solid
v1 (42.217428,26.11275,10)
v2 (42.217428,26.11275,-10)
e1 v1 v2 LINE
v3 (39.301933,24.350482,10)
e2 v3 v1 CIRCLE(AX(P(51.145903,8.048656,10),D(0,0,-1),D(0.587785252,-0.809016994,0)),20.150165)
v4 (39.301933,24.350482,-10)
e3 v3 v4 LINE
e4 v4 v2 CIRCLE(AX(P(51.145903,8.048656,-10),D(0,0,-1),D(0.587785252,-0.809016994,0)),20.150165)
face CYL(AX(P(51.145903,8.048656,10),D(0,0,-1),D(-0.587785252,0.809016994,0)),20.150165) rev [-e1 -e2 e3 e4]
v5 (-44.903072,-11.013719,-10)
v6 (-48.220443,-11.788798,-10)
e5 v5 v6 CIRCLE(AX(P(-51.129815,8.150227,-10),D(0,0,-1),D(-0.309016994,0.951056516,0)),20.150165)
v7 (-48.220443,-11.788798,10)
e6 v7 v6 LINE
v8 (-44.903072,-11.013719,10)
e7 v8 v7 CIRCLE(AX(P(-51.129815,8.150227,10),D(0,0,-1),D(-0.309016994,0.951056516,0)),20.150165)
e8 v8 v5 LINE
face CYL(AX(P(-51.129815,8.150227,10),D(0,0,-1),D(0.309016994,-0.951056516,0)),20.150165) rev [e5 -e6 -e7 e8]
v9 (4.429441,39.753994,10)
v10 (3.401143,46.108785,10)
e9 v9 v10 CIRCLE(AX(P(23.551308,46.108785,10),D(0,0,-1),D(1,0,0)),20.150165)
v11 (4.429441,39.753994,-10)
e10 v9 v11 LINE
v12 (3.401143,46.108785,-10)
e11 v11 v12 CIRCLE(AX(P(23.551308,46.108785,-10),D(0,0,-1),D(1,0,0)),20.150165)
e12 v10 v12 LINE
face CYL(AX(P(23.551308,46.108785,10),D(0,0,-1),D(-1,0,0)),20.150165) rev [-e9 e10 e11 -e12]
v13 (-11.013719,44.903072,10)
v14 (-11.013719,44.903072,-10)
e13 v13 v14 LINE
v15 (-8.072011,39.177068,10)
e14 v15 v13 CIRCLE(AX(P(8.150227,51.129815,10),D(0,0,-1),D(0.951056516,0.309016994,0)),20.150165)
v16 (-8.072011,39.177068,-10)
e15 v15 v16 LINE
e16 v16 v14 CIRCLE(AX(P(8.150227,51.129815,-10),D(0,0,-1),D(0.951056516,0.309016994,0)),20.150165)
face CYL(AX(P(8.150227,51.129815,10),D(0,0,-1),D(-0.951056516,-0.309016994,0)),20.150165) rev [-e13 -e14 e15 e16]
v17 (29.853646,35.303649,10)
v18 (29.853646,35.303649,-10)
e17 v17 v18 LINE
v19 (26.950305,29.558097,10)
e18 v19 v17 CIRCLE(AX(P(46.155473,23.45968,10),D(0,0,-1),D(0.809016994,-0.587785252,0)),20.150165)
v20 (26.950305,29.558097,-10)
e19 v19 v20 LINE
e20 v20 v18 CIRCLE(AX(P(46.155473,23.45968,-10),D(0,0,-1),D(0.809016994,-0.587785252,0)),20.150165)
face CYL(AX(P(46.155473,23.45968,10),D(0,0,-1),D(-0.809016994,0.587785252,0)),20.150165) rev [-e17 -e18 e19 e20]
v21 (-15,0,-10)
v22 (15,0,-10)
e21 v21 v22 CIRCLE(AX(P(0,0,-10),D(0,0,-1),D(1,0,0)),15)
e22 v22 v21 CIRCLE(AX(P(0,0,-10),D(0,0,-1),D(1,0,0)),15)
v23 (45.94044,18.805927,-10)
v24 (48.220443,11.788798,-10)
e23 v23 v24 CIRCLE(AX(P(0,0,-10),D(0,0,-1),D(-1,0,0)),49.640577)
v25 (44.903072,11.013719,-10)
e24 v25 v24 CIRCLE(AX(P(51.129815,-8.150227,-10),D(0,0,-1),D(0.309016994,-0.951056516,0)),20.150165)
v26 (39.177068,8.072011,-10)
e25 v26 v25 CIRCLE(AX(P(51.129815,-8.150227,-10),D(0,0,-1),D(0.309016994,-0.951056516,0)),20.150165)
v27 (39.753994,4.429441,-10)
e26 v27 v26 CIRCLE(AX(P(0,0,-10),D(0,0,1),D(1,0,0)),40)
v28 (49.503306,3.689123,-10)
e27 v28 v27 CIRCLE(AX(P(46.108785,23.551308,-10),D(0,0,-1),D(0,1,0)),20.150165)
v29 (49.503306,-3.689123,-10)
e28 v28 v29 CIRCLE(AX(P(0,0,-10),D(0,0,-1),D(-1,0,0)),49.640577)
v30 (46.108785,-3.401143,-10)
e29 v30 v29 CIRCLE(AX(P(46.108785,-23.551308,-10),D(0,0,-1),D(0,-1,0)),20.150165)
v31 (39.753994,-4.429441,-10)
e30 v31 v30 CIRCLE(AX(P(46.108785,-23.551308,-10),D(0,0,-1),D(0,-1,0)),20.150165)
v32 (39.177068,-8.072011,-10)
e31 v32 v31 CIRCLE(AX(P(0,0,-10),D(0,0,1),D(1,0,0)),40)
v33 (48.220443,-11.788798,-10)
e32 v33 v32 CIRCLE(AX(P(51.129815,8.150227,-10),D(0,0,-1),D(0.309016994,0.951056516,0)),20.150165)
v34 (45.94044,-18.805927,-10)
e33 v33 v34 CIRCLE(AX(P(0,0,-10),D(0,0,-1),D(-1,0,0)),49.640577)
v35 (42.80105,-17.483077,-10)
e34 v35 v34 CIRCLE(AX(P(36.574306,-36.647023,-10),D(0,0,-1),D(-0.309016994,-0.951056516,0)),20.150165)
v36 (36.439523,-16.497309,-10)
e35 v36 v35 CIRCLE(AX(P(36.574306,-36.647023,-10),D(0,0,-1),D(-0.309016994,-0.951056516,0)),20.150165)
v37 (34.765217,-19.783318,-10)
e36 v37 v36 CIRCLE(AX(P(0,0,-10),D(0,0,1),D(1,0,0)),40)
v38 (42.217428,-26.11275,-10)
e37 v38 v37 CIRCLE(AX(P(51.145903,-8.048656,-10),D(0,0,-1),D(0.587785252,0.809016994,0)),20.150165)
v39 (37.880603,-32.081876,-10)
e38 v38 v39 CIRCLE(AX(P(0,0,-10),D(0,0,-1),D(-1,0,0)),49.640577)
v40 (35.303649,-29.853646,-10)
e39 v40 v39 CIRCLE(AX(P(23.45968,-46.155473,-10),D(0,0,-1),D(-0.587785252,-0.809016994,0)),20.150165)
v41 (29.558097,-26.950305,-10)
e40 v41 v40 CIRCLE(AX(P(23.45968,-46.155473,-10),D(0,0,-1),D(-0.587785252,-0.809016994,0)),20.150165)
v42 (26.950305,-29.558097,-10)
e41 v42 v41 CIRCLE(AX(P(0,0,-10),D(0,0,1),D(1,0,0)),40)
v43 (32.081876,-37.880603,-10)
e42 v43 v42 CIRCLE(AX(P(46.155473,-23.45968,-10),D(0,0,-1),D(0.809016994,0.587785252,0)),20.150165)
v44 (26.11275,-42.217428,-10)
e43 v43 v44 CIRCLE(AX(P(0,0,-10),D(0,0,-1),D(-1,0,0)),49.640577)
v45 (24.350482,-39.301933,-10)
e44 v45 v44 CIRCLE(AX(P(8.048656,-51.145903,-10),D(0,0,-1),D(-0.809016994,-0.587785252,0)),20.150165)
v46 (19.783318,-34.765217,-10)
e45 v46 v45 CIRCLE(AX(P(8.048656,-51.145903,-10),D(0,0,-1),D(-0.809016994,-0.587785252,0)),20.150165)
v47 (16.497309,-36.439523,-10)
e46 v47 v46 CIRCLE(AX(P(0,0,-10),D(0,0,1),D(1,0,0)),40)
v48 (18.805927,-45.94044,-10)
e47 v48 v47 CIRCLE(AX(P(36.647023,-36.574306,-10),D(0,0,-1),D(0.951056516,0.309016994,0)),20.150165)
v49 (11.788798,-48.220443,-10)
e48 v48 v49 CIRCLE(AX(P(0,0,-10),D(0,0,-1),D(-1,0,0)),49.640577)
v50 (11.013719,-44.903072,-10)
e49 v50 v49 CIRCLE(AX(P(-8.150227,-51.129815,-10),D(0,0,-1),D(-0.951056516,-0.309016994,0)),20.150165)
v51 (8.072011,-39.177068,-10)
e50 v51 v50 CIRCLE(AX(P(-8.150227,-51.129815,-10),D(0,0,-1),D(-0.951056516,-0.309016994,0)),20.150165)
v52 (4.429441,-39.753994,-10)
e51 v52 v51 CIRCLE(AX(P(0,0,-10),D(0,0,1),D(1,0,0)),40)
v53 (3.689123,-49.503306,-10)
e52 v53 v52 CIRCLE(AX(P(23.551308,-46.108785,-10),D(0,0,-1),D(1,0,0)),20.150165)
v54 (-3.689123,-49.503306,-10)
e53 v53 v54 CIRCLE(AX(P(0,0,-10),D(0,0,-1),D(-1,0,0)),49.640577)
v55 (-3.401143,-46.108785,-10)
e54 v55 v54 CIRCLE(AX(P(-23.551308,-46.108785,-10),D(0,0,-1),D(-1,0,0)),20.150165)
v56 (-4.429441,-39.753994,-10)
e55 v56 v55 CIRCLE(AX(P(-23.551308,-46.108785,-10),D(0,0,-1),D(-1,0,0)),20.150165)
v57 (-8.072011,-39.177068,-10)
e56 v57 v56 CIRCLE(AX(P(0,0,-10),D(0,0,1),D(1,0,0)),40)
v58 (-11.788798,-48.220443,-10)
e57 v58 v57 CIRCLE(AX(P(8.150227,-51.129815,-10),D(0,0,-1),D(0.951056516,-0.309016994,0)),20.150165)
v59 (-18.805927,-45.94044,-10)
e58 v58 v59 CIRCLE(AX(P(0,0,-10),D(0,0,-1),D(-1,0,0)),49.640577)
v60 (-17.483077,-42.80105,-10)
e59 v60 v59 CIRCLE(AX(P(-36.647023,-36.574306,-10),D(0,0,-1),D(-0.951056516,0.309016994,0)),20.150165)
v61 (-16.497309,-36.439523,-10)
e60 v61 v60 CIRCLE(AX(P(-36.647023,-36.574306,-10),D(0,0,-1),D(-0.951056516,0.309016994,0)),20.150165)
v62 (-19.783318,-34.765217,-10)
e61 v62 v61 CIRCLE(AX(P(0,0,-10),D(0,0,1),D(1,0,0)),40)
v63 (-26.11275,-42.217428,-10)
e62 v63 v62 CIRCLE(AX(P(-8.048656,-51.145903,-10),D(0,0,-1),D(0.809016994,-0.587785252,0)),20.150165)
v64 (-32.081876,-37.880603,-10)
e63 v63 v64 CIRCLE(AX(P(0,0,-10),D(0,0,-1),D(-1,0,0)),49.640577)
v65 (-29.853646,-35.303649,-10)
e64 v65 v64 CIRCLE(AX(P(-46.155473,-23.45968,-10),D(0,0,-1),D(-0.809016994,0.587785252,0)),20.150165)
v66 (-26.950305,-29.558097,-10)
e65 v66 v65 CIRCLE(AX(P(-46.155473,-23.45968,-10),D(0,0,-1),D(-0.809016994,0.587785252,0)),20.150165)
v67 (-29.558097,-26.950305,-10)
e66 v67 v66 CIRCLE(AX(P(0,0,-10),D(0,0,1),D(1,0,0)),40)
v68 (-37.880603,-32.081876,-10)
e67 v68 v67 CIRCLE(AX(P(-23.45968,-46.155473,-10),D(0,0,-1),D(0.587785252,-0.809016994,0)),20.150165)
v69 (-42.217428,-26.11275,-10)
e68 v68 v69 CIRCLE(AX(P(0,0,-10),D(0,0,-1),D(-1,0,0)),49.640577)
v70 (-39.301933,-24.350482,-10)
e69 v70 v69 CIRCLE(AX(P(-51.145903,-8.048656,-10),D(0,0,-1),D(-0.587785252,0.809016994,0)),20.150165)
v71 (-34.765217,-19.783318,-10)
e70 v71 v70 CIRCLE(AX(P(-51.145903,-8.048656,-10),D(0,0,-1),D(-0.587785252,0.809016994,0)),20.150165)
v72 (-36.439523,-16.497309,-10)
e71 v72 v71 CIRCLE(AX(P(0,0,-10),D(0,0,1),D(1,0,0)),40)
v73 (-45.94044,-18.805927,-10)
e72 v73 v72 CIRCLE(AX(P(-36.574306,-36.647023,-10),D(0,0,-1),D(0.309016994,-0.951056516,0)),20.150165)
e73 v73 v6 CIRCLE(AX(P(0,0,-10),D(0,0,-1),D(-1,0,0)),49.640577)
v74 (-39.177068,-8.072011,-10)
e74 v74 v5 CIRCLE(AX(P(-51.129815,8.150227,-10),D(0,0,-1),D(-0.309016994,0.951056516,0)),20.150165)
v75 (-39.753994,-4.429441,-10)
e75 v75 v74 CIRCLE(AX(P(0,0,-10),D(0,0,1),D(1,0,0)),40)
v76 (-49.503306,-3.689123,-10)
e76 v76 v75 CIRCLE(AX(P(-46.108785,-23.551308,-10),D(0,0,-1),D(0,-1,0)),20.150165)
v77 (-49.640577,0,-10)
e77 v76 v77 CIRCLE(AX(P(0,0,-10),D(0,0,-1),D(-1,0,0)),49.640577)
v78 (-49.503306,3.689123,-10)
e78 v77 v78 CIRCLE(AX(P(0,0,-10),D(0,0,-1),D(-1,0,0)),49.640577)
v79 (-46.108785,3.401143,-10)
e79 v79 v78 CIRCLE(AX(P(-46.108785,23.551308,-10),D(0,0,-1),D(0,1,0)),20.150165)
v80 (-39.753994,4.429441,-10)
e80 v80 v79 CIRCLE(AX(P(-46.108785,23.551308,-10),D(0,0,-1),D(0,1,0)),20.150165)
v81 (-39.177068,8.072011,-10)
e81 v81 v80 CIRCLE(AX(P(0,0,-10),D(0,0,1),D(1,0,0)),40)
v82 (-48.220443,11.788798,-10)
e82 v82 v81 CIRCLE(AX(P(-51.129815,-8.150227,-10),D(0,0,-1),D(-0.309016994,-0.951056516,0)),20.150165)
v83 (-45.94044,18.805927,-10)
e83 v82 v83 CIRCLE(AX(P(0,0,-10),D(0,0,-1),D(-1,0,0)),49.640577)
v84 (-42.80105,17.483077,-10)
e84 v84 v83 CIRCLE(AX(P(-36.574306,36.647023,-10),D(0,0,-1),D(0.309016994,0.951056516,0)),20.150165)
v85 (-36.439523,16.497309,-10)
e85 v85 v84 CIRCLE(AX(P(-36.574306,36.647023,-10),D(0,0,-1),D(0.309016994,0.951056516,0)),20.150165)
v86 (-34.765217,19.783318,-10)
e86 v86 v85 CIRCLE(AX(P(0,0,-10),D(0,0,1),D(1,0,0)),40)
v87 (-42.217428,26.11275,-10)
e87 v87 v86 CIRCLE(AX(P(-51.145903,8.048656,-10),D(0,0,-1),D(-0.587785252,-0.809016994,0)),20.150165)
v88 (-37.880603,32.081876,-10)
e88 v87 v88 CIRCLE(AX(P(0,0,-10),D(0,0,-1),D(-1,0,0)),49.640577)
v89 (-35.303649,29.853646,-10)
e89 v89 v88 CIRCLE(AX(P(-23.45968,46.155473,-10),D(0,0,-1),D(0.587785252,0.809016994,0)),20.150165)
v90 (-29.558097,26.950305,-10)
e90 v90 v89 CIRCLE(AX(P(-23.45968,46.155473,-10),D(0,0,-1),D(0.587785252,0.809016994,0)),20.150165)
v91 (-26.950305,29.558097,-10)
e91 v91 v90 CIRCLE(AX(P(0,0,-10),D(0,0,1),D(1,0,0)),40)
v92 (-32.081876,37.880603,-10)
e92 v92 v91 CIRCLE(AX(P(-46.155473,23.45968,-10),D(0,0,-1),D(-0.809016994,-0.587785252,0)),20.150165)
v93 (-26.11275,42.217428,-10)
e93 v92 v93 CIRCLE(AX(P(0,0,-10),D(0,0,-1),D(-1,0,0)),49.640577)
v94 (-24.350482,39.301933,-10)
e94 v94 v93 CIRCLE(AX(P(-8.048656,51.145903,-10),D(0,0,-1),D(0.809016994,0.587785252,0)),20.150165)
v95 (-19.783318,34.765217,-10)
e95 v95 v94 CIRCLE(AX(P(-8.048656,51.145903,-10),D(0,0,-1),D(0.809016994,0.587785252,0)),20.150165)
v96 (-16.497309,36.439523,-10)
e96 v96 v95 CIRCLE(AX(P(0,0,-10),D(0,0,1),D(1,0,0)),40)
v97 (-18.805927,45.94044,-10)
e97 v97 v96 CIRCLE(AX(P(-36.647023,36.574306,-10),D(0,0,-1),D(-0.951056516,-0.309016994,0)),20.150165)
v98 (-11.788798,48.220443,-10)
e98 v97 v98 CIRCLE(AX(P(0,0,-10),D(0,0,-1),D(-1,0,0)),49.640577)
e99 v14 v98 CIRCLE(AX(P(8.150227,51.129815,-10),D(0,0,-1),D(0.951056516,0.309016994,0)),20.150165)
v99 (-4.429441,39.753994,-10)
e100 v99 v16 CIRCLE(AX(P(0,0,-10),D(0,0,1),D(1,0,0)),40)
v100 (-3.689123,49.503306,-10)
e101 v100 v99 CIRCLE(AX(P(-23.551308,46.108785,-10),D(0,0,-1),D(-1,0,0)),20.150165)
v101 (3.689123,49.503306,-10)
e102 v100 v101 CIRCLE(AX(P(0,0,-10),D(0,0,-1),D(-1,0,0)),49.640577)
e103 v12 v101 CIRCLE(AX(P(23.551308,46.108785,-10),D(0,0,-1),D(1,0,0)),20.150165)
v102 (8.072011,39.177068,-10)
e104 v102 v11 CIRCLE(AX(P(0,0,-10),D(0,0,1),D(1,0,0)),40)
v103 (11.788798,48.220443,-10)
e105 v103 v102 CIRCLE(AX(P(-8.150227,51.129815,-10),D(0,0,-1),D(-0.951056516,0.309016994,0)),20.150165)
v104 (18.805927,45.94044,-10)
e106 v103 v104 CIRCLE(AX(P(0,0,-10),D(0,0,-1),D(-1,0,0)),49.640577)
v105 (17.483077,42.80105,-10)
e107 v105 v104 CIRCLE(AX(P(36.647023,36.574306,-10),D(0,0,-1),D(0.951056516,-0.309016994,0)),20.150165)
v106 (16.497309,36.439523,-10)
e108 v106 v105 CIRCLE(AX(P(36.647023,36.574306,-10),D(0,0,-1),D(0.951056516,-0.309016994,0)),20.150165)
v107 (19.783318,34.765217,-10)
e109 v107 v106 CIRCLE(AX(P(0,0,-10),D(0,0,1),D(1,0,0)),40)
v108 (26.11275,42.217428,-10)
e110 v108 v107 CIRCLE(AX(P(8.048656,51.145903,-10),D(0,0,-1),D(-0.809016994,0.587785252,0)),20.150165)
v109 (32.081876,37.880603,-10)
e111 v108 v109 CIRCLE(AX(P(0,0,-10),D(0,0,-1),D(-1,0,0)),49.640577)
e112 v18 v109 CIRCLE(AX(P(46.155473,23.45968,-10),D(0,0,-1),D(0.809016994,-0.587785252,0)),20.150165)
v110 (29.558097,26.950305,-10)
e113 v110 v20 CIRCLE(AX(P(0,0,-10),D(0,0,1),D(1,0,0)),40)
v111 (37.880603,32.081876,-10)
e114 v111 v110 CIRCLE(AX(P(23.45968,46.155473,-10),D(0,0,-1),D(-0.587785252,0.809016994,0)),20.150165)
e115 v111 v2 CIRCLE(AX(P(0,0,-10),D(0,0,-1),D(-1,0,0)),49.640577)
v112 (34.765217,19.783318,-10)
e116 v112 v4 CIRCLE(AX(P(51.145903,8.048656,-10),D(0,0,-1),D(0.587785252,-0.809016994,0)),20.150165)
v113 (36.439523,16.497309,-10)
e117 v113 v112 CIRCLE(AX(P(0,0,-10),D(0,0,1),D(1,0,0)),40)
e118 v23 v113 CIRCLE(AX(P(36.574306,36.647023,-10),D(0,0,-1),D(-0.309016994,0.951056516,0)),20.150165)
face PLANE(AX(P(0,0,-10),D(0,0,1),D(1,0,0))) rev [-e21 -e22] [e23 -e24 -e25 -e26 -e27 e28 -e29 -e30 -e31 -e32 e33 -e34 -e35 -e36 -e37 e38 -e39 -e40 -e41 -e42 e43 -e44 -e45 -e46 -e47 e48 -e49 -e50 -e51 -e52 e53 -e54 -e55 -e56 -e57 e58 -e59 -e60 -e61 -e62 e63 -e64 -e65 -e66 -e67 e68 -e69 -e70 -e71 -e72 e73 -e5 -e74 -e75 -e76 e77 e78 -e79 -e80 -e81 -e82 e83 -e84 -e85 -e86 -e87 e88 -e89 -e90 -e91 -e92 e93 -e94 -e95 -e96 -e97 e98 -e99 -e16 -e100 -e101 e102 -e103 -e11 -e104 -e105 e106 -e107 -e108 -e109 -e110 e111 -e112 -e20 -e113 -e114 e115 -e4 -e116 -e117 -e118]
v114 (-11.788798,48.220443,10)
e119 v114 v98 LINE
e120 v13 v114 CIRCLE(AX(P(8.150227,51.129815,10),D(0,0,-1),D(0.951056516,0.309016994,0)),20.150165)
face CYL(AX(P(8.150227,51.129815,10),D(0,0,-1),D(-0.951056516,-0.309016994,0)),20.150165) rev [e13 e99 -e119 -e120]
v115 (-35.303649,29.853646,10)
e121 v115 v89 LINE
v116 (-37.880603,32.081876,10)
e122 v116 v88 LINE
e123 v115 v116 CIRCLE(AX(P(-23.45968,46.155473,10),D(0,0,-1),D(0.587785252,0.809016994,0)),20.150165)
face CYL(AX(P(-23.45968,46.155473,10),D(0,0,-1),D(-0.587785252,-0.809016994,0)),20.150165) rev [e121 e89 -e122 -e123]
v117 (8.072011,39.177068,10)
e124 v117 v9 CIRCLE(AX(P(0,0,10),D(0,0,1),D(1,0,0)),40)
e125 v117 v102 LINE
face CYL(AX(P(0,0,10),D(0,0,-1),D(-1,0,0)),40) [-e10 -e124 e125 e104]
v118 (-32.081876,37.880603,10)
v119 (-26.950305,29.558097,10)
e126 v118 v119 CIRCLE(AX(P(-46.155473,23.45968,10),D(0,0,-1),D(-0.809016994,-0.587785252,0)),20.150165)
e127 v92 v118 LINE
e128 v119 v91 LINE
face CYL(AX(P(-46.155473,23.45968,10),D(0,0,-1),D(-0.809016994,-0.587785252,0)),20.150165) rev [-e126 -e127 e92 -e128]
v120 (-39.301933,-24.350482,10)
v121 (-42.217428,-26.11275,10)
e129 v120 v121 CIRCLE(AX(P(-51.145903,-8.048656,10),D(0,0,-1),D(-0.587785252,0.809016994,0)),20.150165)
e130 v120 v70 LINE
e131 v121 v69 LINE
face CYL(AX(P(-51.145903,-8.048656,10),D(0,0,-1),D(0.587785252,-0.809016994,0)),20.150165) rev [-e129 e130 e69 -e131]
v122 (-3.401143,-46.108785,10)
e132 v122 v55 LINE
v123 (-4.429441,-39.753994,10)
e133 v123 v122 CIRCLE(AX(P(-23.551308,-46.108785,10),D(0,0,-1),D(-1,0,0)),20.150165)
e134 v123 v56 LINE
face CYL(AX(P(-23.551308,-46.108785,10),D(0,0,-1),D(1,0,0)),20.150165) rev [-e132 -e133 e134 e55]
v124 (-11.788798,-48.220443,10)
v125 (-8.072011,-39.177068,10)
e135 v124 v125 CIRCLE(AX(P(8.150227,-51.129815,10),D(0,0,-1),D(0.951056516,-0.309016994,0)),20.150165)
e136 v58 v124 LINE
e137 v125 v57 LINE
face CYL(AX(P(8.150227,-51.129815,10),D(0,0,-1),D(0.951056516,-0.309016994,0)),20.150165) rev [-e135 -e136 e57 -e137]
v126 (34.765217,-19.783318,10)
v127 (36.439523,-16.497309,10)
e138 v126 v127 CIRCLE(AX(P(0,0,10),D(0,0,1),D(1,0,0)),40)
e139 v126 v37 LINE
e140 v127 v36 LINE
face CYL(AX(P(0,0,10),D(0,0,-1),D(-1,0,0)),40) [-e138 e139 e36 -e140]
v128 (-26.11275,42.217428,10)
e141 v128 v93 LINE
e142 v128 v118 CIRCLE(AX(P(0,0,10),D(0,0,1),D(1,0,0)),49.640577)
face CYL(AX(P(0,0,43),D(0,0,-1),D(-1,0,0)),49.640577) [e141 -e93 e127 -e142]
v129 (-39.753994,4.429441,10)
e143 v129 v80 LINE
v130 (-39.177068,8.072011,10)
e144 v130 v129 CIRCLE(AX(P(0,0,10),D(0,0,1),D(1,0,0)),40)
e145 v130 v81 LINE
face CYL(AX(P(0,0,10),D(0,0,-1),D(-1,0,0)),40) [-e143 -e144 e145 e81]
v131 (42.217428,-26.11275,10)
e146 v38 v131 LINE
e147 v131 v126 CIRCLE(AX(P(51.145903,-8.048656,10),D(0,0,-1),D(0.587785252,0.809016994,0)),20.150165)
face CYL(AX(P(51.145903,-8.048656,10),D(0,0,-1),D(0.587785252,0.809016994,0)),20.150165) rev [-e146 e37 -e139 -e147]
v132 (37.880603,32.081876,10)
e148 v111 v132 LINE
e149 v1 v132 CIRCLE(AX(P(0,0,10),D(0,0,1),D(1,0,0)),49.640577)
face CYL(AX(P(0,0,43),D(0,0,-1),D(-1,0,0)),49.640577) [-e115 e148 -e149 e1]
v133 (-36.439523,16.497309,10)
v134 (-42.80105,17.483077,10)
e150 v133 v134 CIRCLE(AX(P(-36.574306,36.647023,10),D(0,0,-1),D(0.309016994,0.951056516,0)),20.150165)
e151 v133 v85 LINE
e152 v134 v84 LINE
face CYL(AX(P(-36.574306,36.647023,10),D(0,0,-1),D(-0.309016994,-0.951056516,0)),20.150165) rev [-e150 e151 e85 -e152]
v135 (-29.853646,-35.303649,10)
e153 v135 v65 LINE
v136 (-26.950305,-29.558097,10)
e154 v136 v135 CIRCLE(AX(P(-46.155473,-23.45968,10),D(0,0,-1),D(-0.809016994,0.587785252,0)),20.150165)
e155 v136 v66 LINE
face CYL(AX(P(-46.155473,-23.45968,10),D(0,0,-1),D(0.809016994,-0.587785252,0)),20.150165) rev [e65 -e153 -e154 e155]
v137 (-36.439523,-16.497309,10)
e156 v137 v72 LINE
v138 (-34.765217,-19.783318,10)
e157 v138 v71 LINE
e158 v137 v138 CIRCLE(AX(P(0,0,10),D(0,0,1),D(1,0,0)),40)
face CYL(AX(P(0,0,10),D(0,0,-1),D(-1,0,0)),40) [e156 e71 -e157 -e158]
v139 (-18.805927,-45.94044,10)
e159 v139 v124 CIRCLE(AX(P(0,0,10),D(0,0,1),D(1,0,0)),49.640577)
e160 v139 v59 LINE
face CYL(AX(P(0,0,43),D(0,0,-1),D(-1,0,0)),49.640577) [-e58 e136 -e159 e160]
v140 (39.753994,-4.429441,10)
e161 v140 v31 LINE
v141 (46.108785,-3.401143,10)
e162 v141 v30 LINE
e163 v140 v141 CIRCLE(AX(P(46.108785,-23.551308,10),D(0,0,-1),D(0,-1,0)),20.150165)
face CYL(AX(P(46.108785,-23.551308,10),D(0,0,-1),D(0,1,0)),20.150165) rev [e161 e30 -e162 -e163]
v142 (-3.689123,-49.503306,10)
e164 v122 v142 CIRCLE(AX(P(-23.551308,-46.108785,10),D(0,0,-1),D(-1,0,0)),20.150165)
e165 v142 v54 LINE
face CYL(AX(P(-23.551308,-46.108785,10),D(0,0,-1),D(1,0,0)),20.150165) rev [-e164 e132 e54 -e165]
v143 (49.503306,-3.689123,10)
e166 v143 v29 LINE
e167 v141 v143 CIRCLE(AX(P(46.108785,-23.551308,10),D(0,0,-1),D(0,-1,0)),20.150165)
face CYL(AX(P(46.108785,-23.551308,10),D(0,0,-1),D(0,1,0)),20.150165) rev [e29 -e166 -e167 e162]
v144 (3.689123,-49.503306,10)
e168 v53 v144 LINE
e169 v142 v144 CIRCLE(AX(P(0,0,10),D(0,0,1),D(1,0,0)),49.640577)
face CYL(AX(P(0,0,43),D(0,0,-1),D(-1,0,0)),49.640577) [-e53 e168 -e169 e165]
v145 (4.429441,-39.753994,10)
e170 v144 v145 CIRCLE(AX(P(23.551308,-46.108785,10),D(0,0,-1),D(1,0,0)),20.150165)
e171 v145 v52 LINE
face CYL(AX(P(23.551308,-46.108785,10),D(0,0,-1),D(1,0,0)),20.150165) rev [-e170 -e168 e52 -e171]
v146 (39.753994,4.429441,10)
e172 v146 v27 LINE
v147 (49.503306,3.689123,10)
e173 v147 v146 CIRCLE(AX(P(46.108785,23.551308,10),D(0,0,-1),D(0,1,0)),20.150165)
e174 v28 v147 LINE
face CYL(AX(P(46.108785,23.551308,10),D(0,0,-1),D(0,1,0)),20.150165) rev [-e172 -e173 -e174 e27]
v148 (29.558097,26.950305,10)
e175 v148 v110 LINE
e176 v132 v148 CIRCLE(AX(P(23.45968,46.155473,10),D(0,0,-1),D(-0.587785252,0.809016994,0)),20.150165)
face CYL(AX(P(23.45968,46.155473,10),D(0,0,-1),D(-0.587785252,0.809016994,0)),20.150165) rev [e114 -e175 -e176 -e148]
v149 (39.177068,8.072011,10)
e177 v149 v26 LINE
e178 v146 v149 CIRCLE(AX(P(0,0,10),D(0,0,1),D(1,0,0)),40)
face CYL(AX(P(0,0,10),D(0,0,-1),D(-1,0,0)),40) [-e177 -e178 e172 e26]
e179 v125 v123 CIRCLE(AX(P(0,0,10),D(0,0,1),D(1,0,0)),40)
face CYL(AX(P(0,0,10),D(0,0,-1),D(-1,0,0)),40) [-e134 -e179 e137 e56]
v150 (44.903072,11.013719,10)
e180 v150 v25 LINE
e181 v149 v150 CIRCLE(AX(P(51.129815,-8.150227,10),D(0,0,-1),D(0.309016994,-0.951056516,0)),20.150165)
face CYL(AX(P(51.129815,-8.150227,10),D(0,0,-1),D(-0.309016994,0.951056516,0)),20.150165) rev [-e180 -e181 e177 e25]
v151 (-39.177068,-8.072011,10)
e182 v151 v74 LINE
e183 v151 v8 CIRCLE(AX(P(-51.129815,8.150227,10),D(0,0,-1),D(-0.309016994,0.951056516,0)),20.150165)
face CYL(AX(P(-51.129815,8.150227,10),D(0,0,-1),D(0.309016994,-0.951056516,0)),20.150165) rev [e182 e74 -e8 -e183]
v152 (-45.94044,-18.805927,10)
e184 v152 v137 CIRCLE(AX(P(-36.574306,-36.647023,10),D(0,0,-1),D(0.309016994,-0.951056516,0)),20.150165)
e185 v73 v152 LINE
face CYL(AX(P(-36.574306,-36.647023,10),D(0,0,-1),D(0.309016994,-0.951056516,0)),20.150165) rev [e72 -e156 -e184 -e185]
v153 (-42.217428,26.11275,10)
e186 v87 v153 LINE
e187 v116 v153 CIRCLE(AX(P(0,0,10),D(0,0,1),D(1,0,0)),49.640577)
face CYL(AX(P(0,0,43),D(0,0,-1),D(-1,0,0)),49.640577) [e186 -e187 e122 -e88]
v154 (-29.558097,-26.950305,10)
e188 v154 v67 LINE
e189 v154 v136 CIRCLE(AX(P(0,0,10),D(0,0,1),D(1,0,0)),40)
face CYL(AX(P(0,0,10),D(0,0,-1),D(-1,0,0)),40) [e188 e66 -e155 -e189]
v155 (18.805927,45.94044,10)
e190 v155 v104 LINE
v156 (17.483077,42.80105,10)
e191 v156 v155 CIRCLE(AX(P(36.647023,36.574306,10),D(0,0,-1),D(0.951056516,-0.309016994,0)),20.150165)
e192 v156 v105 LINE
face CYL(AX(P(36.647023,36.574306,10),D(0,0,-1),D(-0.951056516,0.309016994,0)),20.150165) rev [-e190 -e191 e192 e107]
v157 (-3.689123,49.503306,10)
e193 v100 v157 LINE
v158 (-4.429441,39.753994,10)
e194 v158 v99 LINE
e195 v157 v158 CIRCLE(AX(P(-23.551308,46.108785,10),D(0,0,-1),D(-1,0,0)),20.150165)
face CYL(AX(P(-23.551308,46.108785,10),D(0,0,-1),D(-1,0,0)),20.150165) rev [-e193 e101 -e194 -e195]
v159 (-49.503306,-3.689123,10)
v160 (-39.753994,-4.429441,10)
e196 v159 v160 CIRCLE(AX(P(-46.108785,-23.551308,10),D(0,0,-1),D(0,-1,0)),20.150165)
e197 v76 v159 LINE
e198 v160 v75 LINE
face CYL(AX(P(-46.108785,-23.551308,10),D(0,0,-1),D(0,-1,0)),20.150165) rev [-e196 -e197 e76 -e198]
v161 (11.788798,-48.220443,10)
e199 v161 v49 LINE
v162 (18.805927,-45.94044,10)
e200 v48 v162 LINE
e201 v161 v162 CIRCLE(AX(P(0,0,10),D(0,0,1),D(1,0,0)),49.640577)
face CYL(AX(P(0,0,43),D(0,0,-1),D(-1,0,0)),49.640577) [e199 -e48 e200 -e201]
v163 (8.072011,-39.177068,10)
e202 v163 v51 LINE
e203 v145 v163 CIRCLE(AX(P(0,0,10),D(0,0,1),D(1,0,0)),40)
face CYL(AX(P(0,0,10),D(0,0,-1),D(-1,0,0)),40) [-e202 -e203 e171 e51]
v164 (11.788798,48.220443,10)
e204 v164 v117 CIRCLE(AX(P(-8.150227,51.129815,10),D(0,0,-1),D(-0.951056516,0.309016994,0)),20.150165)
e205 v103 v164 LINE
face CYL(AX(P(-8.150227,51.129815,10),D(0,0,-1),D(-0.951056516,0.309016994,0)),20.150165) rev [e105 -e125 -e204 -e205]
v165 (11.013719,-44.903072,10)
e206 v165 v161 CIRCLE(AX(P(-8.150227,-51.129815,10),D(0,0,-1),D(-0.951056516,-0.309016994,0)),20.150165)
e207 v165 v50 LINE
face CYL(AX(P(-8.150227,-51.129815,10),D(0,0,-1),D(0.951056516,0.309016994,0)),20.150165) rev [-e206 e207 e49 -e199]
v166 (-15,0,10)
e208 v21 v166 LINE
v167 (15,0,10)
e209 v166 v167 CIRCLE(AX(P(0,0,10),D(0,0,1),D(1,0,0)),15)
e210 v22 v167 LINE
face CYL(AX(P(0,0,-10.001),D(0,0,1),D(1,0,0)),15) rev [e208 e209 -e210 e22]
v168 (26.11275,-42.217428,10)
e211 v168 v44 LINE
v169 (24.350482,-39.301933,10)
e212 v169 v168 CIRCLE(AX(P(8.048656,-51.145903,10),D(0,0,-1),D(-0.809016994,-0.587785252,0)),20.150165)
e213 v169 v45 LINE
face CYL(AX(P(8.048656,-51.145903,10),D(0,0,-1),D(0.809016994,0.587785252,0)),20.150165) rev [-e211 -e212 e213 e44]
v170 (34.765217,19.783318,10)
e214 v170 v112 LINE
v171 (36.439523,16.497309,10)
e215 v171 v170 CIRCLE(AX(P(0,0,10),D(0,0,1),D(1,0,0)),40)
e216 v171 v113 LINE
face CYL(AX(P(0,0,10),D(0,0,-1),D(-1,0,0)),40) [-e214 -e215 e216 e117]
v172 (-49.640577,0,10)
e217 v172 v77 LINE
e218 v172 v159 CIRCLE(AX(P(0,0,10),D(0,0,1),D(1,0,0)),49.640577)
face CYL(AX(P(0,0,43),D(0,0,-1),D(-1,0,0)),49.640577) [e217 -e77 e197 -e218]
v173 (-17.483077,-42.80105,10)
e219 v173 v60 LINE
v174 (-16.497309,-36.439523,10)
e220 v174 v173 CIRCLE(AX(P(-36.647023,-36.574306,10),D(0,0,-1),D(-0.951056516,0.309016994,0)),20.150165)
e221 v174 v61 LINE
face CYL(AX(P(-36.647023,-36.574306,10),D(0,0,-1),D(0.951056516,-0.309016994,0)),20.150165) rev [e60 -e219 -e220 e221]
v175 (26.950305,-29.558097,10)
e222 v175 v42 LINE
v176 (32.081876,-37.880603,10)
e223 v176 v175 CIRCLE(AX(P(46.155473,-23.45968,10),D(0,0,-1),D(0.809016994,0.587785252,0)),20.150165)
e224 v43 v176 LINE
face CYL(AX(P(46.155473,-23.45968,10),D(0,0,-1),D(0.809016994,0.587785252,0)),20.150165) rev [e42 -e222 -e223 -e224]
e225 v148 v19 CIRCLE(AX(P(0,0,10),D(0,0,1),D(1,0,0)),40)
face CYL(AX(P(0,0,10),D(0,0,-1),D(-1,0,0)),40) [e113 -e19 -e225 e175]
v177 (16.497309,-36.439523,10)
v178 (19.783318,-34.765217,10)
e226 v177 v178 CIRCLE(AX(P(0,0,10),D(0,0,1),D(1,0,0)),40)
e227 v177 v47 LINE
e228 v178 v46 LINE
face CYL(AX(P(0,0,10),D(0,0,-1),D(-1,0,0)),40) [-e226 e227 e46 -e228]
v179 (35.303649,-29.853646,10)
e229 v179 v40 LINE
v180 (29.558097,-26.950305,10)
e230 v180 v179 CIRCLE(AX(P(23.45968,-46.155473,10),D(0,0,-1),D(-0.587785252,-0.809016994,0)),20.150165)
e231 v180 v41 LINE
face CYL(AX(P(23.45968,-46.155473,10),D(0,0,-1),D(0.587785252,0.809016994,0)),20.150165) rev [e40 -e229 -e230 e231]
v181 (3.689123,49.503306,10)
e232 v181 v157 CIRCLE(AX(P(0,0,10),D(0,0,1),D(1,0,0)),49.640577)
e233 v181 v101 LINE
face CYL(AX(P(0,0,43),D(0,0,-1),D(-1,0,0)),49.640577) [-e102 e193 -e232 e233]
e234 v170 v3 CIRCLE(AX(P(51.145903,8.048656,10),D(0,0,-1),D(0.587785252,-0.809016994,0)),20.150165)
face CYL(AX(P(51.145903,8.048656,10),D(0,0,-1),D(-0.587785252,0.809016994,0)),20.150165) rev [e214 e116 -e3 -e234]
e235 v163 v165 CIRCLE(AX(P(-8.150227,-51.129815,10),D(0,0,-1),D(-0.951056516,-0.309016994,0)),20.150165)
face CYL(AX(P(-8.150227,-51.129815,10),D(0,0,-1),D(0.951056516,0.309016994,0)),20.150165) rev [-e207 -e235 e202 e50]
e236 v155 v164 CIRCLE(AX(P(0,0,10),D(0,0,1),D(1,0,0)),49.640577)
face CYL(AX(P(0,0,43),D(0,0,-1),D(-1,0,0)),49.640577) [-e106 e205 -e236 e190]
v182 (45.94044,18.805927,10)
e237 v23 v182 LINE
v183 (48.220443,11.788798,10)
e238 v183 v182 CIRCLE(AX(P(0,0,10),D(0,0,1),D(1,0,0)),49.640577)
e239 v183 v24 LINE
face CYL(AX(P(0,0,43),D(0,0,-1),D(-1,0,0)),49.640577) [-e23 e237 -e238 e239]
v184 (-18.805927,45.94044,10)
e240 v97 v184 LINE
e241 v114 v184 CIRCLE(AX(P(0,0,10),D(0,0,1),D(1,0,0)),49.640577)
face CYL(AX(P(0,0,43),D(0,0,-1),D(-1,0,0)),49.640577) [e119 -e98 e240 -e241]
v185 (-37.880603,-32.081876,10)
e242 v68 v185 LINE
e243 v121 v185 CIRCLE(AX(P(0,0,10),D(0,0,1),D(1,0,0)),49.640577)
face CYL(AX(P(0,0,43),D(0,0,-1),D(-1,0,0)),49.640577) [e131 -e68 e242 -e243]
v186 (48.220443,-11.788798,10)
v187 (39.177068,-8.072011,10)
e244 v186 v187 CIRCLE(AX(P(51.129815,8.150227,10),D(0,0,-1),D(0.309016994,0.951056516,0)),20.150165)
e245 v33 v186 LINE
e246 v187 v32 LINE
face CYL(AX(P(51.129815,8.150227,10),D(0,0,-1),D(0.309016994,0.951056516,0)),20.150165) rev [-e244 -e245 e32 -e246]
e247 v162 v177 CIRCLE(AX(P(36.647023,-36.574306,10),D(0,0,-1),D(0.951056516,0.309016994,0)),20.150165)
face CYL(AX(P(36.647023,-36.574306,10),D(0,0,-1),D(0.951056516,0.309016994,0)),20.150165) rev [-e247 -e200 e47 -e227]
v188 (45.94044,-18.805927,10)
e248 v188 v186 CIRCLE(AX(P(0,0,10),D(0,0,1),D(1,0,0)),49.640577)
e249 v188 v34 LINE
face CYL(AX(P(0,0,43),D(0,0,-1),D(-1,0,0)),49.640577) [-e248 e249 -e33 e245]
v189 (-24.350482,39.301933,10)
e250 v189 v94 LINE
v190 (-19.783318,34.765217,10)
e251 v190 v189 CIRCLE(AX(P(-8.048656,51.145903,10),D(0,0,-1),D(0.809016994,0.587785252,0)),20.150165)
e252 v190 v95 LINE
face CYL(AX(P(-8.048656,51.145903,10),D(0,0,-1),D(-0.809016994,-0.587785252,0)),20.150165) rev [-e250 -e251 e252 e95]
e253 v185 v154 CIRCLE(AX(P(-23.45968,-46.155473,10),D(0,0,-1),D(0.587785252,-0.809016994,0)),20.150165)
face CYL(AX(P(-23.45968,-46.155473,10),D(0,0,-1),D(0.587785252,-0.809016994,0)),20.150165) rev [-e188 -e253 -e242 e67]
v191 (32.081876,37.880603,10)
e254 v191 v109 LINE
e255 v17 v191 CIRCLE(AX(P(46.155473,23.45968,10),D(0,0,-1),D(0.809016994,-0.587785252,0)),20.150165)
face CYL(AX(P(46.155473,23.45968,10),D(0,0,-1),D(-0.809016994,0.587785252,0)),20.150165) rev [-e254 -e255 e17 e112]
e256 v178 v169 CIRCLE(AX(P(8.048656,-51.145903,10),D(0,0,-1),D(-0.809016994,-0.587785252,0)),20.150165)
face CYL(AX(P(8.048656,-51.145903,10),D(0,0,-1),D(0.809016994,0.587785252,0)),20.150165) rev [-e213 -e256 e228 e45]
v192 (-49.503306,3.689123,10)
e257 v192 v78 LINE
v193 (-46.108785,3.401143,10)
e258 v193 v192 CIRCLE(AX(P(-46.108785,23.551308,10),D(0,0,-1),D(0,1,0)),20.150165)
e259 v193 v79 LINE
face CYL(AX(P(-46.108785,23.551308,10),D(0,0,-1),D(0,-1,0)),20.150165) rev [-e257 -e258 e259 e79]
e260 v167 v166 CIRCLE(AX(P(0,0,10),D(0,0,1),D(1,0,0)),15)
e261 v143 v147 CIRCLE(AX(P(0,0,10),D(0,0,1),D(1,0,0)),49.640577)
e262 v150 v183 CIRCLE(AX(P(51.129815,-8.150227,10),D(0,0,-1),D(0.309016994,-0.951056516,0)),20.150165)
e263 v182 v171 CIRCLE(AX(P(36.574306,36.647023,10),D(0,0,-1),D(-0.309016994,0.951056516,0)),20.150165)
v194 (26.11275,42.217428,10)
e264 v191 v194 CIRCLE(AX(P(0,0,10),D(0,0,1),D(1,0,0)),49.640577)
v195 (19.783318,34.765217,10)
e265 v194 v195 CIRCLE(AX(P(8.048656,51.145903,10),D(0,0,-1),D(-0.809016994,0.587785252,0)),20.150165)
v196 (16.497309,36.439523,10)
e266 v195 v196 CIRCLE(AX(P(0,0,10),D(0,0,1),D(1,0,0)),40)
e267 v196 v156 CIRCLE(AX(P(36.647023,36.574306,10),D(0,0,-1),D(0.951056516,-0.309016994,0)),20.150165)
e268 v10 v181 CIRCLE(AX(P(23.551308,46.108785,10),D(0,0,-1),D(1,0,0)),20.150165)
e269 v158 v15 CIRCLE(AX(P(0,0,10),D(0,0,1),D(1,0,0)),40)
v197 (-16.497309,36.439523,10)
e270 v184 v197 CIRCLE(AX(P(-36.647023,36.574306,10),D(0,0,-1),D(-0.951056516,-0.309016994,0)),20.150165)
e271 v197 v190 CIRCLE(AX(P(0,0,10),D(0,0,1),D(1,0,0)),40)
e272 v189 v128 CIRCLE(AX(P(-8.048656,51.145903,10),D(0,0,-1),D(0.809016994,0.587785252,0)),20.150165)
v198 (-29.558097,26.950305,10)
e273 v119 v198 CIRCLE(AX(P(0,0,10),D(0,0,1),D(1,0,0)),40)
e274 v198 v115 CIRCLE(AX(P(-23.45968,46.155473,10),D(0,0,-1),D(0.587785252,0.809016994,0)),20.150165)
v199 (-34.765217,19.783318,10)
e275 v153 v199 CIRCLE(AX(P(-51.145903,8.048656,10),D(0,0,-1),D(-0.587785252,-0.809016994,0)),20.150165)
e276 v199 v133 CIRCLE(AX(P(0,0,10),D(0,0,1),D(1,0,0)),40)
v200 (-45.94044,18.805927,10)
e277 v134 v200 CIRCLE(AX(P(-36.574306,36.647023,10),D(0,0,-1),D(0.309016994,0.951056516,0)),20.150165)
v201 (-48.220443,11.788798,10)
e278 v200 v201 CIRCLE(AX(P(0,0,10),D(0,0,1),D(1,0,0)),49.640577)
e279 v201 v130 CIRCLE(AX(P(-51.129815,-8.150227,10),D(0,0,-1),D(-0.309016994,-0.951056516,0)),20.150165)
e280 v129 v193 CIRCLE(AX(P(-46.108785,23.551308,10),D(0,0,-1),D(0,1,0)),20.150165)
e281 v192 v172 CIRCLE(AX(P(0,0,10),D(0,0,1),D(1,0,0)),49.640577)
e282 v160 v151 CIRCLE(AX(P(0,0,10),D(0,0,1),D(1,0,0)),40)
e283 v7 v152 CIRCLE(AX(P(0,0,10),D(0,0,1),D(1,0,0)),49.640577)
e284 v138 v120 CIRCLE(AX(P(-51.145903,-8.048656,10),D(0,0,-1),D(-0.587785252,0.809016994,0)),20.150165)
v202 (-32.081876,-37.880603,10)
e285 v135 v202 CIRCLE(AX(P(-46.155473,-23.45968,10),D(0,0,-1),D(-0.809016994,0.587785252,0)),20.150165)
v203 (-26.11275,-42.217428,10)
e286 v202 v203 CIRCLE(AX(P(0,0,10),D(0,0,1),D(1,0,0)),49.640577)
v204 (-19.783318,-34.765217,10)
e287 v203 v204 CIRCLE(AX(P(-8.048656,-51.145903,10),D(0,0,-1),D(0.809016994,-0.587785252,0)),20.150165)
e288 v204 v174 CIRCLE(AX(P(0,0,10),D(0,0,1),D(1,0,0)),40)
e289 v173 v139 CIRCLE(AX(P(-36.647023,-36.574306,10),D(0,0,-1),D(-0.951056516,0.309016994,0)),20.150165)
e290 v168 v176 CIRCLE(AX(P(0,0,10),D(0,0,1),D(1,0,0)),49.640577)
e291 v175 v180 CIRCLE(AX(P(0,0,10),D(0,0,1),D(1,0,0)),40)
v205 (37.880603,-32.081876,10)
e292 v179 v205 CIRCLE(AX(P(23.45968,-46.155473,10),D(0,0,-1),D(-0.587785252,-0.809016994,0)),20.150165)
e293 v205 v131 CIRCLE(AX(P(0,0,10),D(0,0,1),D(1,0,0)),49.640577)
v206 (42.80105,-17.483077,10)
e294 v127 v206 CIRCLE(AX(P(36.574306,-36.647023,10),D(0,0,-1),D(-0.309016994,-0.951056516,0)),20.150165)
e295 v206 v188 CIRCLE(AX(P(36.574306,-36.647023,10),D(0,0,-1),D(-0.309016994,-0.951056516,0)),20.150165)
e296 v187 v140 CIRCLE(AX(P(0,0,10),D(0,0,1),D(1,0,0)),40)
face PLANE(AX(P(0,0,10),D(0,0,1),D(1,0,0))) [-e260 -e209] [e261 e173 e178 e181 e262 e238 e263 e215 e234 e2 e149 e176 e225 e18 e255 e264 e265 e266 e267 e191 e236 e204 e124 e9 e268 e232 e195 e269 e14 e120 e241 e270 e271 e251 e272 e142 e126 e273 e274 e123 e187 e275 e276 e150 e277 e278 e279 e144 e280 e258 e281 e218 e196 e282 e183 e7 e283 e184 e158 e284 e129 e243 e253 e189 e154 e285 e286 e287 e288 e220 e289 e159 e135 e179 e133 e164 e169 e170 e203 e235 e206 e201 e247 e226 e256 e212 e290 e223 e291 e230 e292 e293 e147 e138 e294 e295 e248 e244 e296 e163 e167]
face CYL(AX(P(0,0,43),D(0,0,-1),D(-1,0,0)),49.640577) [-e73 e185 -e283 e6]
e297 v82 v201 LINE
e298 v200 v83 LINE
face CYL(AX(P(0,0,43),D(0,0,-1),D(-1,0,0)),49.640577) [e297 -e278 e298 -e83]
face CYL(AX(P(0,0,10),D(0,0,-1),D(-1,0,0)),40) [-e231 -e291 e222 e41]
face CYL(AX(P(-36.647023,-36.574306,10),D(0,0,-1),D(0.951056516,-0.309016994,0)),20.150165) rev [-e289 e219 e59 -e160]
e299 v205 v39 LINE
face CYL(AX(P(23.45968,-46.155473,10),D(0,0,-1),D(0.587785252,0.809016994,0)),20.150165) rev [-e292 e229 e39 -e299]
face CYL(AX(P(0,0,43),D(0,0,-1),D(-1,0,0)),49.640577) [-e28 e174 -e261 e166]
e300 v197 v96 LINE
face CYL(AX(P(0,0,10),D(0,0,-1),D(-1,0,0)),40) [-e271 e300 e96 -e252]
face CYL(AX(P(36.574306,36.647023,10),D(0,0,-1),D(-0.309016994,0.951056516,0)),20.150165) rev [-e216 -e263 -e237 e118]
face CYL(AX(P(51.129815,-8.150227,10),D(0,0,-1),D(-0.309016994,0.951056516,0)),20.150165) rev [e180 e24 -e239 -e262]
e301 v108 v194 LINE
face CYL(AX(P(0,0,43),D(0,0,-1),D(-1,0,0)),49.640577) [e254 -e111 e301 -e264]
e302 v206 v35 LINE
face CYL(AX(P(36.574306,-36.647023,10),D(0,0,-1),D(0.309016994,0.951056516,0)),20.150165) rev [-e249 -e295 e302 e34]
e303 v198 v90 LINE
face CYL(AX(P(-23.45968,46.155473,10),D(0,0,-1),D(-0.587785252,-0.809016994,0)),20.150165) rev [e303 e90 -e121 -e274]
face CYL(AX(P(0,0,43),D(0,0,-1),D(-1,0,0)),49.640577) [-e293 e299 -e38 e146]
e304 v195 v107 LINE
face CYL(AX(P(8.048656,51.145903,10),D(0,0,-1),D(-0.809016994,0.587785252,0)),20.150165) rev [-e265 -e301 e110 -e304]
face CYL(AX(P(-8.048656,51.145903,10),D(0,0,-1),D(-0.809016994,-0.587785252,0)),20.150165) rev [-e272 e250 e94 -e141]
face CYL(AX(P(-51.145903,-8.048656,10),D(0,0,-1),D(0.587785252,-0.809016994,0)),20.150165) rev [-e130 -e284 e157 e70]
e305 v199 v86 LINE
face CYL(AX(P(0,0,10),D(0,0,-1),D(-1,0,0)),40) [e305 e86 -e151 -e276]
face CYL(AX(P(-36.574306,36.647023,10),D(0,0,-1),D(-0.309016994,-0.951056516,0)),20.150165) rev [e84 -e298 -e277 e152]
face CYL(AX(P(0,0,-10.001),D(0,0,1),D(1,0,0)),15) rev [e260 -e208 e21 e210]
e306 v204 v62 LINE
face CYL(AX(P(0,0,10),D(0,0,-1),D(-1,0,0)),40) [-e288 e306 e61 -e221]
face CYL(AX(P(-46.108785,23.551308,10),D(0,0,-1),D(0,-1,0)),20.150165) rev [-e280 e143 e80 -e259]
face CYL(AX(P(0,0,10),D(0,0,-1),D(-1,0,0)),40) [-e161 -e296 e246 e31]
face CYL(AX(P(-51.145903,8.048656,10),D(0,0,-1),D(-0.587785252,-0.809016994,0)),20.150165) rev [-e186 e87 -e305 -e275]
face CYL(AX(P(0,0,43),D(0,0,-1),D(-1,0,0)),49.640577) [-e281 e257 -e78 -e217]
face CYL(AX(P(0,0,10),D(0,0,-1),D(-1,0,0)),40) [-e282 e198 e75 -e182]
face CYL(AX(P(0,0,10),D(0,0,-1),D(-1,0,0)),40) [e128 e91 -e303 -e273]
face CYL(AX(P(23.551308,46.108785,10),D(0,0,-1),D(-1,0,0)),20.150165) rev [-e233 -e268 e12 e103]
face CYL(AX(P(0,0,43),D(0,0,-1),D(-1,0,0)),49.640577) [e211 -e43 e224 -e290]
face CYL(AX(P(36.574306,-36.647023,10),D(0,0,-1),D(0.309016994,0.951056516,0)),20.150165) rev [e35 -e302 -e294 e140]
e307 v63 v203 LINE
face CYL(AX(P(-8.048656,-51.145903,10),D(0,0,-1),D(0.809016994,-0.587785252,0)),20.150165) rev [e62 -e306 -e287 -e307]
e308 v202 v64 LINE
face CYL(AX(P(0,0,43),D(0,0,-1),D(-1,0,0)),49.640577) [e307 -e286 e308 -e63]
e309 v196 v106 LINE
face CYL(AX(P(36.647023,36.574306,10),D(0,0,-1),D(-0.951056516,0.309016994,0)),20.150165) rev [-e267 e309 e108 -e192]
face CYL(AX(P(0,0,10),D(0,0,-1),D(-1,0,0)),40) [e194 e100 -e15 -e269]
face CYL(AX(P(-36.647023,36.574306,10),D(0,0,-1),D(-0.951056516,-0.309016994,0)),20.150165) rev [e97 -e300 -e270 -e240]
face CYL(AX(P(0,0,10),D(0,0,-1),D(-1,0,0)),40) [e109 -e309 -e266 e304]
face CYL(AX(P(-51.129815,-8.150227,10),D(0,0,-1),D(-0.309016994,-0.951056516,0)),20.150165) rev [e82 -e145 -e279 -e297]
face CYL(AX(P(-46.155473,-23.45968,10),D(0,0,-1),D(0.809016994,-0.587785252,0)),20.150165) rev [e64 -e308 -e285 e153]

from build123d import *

# Parameters (mm, degrees)
SKETCH1_R           = 40
BOSS_EXTRUDE1_DEPTH = 10
CUT_EXTRUDE1_REACH  = 62
SKETCH2_R           = 15
BOSS_EXTRUDE2_DEPTH = 10
CIRPATTERN1_COUNT   = 20
SKETCH5_OUTSIDE_W   = 133.242
SKETCH5_OUTSIDE_H   = 133.242
SKETCH5_OUTSIDE_R   = 49.640577174
CUT_EXTRUDE4_DEPTH  = 53


with BuildPart() as part:
    # Sketch1 → Boss-Extrude1 (new, symmetric)
    with BuildSketch(Plane.XY):
        Circle(SKETCH1_R)
    extrude(amount=BOSS_EXTRUDE1_DEPTH, both=True)

    # Sketch2 → Cut-Extrude1 (cut, up to next)
    with BuildSketch(Plane.XY.offset(10), mode=Mode.PRIVATE) as cut_extrude1_sk1:
        Circle(SKETCH2_R)
    cut_extrude1_tool1 = extrude(cut_extrude1_sk1.sketch, amount=-CUT_EXTRUDE1_REACH, mode=Mode.PRIVATE) & part.part
    add(cut_extrude1_tool1.solids().sort_by_distance((0, 0, 10))[0], mode=Mode.SUBTRACT)

    # Sketch4 → Boss-Extrude2 (add, symmetric)
    with BuildSketch(Plane.XY):
        with BuildLine():
            ThreePointArc((3.963482067, 50.835965639), (3.418931143, 45.262287362), (4.429441361, 39.753994129))
            ThreePointArc((4.429441361, 39.753994129), (0, 40), (-4.429441361, 39.753994129))
            ThreePointArc((-4.429441361, 39.753994129), (-3.418931143, 45.262287362), (-3.963482067, 50.835965639))
            ThreePointArc((-3.963482067, 50.835965639), (0, 51.045354515), (3.963482067, 50.835965639))
        make_face()
    boss_extrude2 = extrude(amount=BOSS_EXTRUDE2_DEPTH, both=True)

    # CirPattern1: Boss-Extrude2 ×20 about axis
    cirpattern1_axis = Axis((0, 0, 0), (0, 0, 1))
    for i in range(1, CIRPATTERN1_COUNT):
        add(boss_extrude2.rotate(cirpattern1_axis, i * 360 / CIRPATTERN1_COUNT))

    # Sketch5 outside → Cut-Extrude4 (cut)
    with BuildSketch(Plane(origin=(0, 0, -10), x_dir=(-1, 0, 0), z_dir=(0, 0, -1))):
        Rectangle(SKETCH5_OUTSIDE_W, SKETCH5_OUTSIDE_H)
        Circle(SKETCH5_OUTSIDE_R, mode=Mode.SUBTRACT)
    extrude(amount=-CUT_EXTRUDE4_DEPTH, mode=Mode.SUBTRACT)


solid = part.part
